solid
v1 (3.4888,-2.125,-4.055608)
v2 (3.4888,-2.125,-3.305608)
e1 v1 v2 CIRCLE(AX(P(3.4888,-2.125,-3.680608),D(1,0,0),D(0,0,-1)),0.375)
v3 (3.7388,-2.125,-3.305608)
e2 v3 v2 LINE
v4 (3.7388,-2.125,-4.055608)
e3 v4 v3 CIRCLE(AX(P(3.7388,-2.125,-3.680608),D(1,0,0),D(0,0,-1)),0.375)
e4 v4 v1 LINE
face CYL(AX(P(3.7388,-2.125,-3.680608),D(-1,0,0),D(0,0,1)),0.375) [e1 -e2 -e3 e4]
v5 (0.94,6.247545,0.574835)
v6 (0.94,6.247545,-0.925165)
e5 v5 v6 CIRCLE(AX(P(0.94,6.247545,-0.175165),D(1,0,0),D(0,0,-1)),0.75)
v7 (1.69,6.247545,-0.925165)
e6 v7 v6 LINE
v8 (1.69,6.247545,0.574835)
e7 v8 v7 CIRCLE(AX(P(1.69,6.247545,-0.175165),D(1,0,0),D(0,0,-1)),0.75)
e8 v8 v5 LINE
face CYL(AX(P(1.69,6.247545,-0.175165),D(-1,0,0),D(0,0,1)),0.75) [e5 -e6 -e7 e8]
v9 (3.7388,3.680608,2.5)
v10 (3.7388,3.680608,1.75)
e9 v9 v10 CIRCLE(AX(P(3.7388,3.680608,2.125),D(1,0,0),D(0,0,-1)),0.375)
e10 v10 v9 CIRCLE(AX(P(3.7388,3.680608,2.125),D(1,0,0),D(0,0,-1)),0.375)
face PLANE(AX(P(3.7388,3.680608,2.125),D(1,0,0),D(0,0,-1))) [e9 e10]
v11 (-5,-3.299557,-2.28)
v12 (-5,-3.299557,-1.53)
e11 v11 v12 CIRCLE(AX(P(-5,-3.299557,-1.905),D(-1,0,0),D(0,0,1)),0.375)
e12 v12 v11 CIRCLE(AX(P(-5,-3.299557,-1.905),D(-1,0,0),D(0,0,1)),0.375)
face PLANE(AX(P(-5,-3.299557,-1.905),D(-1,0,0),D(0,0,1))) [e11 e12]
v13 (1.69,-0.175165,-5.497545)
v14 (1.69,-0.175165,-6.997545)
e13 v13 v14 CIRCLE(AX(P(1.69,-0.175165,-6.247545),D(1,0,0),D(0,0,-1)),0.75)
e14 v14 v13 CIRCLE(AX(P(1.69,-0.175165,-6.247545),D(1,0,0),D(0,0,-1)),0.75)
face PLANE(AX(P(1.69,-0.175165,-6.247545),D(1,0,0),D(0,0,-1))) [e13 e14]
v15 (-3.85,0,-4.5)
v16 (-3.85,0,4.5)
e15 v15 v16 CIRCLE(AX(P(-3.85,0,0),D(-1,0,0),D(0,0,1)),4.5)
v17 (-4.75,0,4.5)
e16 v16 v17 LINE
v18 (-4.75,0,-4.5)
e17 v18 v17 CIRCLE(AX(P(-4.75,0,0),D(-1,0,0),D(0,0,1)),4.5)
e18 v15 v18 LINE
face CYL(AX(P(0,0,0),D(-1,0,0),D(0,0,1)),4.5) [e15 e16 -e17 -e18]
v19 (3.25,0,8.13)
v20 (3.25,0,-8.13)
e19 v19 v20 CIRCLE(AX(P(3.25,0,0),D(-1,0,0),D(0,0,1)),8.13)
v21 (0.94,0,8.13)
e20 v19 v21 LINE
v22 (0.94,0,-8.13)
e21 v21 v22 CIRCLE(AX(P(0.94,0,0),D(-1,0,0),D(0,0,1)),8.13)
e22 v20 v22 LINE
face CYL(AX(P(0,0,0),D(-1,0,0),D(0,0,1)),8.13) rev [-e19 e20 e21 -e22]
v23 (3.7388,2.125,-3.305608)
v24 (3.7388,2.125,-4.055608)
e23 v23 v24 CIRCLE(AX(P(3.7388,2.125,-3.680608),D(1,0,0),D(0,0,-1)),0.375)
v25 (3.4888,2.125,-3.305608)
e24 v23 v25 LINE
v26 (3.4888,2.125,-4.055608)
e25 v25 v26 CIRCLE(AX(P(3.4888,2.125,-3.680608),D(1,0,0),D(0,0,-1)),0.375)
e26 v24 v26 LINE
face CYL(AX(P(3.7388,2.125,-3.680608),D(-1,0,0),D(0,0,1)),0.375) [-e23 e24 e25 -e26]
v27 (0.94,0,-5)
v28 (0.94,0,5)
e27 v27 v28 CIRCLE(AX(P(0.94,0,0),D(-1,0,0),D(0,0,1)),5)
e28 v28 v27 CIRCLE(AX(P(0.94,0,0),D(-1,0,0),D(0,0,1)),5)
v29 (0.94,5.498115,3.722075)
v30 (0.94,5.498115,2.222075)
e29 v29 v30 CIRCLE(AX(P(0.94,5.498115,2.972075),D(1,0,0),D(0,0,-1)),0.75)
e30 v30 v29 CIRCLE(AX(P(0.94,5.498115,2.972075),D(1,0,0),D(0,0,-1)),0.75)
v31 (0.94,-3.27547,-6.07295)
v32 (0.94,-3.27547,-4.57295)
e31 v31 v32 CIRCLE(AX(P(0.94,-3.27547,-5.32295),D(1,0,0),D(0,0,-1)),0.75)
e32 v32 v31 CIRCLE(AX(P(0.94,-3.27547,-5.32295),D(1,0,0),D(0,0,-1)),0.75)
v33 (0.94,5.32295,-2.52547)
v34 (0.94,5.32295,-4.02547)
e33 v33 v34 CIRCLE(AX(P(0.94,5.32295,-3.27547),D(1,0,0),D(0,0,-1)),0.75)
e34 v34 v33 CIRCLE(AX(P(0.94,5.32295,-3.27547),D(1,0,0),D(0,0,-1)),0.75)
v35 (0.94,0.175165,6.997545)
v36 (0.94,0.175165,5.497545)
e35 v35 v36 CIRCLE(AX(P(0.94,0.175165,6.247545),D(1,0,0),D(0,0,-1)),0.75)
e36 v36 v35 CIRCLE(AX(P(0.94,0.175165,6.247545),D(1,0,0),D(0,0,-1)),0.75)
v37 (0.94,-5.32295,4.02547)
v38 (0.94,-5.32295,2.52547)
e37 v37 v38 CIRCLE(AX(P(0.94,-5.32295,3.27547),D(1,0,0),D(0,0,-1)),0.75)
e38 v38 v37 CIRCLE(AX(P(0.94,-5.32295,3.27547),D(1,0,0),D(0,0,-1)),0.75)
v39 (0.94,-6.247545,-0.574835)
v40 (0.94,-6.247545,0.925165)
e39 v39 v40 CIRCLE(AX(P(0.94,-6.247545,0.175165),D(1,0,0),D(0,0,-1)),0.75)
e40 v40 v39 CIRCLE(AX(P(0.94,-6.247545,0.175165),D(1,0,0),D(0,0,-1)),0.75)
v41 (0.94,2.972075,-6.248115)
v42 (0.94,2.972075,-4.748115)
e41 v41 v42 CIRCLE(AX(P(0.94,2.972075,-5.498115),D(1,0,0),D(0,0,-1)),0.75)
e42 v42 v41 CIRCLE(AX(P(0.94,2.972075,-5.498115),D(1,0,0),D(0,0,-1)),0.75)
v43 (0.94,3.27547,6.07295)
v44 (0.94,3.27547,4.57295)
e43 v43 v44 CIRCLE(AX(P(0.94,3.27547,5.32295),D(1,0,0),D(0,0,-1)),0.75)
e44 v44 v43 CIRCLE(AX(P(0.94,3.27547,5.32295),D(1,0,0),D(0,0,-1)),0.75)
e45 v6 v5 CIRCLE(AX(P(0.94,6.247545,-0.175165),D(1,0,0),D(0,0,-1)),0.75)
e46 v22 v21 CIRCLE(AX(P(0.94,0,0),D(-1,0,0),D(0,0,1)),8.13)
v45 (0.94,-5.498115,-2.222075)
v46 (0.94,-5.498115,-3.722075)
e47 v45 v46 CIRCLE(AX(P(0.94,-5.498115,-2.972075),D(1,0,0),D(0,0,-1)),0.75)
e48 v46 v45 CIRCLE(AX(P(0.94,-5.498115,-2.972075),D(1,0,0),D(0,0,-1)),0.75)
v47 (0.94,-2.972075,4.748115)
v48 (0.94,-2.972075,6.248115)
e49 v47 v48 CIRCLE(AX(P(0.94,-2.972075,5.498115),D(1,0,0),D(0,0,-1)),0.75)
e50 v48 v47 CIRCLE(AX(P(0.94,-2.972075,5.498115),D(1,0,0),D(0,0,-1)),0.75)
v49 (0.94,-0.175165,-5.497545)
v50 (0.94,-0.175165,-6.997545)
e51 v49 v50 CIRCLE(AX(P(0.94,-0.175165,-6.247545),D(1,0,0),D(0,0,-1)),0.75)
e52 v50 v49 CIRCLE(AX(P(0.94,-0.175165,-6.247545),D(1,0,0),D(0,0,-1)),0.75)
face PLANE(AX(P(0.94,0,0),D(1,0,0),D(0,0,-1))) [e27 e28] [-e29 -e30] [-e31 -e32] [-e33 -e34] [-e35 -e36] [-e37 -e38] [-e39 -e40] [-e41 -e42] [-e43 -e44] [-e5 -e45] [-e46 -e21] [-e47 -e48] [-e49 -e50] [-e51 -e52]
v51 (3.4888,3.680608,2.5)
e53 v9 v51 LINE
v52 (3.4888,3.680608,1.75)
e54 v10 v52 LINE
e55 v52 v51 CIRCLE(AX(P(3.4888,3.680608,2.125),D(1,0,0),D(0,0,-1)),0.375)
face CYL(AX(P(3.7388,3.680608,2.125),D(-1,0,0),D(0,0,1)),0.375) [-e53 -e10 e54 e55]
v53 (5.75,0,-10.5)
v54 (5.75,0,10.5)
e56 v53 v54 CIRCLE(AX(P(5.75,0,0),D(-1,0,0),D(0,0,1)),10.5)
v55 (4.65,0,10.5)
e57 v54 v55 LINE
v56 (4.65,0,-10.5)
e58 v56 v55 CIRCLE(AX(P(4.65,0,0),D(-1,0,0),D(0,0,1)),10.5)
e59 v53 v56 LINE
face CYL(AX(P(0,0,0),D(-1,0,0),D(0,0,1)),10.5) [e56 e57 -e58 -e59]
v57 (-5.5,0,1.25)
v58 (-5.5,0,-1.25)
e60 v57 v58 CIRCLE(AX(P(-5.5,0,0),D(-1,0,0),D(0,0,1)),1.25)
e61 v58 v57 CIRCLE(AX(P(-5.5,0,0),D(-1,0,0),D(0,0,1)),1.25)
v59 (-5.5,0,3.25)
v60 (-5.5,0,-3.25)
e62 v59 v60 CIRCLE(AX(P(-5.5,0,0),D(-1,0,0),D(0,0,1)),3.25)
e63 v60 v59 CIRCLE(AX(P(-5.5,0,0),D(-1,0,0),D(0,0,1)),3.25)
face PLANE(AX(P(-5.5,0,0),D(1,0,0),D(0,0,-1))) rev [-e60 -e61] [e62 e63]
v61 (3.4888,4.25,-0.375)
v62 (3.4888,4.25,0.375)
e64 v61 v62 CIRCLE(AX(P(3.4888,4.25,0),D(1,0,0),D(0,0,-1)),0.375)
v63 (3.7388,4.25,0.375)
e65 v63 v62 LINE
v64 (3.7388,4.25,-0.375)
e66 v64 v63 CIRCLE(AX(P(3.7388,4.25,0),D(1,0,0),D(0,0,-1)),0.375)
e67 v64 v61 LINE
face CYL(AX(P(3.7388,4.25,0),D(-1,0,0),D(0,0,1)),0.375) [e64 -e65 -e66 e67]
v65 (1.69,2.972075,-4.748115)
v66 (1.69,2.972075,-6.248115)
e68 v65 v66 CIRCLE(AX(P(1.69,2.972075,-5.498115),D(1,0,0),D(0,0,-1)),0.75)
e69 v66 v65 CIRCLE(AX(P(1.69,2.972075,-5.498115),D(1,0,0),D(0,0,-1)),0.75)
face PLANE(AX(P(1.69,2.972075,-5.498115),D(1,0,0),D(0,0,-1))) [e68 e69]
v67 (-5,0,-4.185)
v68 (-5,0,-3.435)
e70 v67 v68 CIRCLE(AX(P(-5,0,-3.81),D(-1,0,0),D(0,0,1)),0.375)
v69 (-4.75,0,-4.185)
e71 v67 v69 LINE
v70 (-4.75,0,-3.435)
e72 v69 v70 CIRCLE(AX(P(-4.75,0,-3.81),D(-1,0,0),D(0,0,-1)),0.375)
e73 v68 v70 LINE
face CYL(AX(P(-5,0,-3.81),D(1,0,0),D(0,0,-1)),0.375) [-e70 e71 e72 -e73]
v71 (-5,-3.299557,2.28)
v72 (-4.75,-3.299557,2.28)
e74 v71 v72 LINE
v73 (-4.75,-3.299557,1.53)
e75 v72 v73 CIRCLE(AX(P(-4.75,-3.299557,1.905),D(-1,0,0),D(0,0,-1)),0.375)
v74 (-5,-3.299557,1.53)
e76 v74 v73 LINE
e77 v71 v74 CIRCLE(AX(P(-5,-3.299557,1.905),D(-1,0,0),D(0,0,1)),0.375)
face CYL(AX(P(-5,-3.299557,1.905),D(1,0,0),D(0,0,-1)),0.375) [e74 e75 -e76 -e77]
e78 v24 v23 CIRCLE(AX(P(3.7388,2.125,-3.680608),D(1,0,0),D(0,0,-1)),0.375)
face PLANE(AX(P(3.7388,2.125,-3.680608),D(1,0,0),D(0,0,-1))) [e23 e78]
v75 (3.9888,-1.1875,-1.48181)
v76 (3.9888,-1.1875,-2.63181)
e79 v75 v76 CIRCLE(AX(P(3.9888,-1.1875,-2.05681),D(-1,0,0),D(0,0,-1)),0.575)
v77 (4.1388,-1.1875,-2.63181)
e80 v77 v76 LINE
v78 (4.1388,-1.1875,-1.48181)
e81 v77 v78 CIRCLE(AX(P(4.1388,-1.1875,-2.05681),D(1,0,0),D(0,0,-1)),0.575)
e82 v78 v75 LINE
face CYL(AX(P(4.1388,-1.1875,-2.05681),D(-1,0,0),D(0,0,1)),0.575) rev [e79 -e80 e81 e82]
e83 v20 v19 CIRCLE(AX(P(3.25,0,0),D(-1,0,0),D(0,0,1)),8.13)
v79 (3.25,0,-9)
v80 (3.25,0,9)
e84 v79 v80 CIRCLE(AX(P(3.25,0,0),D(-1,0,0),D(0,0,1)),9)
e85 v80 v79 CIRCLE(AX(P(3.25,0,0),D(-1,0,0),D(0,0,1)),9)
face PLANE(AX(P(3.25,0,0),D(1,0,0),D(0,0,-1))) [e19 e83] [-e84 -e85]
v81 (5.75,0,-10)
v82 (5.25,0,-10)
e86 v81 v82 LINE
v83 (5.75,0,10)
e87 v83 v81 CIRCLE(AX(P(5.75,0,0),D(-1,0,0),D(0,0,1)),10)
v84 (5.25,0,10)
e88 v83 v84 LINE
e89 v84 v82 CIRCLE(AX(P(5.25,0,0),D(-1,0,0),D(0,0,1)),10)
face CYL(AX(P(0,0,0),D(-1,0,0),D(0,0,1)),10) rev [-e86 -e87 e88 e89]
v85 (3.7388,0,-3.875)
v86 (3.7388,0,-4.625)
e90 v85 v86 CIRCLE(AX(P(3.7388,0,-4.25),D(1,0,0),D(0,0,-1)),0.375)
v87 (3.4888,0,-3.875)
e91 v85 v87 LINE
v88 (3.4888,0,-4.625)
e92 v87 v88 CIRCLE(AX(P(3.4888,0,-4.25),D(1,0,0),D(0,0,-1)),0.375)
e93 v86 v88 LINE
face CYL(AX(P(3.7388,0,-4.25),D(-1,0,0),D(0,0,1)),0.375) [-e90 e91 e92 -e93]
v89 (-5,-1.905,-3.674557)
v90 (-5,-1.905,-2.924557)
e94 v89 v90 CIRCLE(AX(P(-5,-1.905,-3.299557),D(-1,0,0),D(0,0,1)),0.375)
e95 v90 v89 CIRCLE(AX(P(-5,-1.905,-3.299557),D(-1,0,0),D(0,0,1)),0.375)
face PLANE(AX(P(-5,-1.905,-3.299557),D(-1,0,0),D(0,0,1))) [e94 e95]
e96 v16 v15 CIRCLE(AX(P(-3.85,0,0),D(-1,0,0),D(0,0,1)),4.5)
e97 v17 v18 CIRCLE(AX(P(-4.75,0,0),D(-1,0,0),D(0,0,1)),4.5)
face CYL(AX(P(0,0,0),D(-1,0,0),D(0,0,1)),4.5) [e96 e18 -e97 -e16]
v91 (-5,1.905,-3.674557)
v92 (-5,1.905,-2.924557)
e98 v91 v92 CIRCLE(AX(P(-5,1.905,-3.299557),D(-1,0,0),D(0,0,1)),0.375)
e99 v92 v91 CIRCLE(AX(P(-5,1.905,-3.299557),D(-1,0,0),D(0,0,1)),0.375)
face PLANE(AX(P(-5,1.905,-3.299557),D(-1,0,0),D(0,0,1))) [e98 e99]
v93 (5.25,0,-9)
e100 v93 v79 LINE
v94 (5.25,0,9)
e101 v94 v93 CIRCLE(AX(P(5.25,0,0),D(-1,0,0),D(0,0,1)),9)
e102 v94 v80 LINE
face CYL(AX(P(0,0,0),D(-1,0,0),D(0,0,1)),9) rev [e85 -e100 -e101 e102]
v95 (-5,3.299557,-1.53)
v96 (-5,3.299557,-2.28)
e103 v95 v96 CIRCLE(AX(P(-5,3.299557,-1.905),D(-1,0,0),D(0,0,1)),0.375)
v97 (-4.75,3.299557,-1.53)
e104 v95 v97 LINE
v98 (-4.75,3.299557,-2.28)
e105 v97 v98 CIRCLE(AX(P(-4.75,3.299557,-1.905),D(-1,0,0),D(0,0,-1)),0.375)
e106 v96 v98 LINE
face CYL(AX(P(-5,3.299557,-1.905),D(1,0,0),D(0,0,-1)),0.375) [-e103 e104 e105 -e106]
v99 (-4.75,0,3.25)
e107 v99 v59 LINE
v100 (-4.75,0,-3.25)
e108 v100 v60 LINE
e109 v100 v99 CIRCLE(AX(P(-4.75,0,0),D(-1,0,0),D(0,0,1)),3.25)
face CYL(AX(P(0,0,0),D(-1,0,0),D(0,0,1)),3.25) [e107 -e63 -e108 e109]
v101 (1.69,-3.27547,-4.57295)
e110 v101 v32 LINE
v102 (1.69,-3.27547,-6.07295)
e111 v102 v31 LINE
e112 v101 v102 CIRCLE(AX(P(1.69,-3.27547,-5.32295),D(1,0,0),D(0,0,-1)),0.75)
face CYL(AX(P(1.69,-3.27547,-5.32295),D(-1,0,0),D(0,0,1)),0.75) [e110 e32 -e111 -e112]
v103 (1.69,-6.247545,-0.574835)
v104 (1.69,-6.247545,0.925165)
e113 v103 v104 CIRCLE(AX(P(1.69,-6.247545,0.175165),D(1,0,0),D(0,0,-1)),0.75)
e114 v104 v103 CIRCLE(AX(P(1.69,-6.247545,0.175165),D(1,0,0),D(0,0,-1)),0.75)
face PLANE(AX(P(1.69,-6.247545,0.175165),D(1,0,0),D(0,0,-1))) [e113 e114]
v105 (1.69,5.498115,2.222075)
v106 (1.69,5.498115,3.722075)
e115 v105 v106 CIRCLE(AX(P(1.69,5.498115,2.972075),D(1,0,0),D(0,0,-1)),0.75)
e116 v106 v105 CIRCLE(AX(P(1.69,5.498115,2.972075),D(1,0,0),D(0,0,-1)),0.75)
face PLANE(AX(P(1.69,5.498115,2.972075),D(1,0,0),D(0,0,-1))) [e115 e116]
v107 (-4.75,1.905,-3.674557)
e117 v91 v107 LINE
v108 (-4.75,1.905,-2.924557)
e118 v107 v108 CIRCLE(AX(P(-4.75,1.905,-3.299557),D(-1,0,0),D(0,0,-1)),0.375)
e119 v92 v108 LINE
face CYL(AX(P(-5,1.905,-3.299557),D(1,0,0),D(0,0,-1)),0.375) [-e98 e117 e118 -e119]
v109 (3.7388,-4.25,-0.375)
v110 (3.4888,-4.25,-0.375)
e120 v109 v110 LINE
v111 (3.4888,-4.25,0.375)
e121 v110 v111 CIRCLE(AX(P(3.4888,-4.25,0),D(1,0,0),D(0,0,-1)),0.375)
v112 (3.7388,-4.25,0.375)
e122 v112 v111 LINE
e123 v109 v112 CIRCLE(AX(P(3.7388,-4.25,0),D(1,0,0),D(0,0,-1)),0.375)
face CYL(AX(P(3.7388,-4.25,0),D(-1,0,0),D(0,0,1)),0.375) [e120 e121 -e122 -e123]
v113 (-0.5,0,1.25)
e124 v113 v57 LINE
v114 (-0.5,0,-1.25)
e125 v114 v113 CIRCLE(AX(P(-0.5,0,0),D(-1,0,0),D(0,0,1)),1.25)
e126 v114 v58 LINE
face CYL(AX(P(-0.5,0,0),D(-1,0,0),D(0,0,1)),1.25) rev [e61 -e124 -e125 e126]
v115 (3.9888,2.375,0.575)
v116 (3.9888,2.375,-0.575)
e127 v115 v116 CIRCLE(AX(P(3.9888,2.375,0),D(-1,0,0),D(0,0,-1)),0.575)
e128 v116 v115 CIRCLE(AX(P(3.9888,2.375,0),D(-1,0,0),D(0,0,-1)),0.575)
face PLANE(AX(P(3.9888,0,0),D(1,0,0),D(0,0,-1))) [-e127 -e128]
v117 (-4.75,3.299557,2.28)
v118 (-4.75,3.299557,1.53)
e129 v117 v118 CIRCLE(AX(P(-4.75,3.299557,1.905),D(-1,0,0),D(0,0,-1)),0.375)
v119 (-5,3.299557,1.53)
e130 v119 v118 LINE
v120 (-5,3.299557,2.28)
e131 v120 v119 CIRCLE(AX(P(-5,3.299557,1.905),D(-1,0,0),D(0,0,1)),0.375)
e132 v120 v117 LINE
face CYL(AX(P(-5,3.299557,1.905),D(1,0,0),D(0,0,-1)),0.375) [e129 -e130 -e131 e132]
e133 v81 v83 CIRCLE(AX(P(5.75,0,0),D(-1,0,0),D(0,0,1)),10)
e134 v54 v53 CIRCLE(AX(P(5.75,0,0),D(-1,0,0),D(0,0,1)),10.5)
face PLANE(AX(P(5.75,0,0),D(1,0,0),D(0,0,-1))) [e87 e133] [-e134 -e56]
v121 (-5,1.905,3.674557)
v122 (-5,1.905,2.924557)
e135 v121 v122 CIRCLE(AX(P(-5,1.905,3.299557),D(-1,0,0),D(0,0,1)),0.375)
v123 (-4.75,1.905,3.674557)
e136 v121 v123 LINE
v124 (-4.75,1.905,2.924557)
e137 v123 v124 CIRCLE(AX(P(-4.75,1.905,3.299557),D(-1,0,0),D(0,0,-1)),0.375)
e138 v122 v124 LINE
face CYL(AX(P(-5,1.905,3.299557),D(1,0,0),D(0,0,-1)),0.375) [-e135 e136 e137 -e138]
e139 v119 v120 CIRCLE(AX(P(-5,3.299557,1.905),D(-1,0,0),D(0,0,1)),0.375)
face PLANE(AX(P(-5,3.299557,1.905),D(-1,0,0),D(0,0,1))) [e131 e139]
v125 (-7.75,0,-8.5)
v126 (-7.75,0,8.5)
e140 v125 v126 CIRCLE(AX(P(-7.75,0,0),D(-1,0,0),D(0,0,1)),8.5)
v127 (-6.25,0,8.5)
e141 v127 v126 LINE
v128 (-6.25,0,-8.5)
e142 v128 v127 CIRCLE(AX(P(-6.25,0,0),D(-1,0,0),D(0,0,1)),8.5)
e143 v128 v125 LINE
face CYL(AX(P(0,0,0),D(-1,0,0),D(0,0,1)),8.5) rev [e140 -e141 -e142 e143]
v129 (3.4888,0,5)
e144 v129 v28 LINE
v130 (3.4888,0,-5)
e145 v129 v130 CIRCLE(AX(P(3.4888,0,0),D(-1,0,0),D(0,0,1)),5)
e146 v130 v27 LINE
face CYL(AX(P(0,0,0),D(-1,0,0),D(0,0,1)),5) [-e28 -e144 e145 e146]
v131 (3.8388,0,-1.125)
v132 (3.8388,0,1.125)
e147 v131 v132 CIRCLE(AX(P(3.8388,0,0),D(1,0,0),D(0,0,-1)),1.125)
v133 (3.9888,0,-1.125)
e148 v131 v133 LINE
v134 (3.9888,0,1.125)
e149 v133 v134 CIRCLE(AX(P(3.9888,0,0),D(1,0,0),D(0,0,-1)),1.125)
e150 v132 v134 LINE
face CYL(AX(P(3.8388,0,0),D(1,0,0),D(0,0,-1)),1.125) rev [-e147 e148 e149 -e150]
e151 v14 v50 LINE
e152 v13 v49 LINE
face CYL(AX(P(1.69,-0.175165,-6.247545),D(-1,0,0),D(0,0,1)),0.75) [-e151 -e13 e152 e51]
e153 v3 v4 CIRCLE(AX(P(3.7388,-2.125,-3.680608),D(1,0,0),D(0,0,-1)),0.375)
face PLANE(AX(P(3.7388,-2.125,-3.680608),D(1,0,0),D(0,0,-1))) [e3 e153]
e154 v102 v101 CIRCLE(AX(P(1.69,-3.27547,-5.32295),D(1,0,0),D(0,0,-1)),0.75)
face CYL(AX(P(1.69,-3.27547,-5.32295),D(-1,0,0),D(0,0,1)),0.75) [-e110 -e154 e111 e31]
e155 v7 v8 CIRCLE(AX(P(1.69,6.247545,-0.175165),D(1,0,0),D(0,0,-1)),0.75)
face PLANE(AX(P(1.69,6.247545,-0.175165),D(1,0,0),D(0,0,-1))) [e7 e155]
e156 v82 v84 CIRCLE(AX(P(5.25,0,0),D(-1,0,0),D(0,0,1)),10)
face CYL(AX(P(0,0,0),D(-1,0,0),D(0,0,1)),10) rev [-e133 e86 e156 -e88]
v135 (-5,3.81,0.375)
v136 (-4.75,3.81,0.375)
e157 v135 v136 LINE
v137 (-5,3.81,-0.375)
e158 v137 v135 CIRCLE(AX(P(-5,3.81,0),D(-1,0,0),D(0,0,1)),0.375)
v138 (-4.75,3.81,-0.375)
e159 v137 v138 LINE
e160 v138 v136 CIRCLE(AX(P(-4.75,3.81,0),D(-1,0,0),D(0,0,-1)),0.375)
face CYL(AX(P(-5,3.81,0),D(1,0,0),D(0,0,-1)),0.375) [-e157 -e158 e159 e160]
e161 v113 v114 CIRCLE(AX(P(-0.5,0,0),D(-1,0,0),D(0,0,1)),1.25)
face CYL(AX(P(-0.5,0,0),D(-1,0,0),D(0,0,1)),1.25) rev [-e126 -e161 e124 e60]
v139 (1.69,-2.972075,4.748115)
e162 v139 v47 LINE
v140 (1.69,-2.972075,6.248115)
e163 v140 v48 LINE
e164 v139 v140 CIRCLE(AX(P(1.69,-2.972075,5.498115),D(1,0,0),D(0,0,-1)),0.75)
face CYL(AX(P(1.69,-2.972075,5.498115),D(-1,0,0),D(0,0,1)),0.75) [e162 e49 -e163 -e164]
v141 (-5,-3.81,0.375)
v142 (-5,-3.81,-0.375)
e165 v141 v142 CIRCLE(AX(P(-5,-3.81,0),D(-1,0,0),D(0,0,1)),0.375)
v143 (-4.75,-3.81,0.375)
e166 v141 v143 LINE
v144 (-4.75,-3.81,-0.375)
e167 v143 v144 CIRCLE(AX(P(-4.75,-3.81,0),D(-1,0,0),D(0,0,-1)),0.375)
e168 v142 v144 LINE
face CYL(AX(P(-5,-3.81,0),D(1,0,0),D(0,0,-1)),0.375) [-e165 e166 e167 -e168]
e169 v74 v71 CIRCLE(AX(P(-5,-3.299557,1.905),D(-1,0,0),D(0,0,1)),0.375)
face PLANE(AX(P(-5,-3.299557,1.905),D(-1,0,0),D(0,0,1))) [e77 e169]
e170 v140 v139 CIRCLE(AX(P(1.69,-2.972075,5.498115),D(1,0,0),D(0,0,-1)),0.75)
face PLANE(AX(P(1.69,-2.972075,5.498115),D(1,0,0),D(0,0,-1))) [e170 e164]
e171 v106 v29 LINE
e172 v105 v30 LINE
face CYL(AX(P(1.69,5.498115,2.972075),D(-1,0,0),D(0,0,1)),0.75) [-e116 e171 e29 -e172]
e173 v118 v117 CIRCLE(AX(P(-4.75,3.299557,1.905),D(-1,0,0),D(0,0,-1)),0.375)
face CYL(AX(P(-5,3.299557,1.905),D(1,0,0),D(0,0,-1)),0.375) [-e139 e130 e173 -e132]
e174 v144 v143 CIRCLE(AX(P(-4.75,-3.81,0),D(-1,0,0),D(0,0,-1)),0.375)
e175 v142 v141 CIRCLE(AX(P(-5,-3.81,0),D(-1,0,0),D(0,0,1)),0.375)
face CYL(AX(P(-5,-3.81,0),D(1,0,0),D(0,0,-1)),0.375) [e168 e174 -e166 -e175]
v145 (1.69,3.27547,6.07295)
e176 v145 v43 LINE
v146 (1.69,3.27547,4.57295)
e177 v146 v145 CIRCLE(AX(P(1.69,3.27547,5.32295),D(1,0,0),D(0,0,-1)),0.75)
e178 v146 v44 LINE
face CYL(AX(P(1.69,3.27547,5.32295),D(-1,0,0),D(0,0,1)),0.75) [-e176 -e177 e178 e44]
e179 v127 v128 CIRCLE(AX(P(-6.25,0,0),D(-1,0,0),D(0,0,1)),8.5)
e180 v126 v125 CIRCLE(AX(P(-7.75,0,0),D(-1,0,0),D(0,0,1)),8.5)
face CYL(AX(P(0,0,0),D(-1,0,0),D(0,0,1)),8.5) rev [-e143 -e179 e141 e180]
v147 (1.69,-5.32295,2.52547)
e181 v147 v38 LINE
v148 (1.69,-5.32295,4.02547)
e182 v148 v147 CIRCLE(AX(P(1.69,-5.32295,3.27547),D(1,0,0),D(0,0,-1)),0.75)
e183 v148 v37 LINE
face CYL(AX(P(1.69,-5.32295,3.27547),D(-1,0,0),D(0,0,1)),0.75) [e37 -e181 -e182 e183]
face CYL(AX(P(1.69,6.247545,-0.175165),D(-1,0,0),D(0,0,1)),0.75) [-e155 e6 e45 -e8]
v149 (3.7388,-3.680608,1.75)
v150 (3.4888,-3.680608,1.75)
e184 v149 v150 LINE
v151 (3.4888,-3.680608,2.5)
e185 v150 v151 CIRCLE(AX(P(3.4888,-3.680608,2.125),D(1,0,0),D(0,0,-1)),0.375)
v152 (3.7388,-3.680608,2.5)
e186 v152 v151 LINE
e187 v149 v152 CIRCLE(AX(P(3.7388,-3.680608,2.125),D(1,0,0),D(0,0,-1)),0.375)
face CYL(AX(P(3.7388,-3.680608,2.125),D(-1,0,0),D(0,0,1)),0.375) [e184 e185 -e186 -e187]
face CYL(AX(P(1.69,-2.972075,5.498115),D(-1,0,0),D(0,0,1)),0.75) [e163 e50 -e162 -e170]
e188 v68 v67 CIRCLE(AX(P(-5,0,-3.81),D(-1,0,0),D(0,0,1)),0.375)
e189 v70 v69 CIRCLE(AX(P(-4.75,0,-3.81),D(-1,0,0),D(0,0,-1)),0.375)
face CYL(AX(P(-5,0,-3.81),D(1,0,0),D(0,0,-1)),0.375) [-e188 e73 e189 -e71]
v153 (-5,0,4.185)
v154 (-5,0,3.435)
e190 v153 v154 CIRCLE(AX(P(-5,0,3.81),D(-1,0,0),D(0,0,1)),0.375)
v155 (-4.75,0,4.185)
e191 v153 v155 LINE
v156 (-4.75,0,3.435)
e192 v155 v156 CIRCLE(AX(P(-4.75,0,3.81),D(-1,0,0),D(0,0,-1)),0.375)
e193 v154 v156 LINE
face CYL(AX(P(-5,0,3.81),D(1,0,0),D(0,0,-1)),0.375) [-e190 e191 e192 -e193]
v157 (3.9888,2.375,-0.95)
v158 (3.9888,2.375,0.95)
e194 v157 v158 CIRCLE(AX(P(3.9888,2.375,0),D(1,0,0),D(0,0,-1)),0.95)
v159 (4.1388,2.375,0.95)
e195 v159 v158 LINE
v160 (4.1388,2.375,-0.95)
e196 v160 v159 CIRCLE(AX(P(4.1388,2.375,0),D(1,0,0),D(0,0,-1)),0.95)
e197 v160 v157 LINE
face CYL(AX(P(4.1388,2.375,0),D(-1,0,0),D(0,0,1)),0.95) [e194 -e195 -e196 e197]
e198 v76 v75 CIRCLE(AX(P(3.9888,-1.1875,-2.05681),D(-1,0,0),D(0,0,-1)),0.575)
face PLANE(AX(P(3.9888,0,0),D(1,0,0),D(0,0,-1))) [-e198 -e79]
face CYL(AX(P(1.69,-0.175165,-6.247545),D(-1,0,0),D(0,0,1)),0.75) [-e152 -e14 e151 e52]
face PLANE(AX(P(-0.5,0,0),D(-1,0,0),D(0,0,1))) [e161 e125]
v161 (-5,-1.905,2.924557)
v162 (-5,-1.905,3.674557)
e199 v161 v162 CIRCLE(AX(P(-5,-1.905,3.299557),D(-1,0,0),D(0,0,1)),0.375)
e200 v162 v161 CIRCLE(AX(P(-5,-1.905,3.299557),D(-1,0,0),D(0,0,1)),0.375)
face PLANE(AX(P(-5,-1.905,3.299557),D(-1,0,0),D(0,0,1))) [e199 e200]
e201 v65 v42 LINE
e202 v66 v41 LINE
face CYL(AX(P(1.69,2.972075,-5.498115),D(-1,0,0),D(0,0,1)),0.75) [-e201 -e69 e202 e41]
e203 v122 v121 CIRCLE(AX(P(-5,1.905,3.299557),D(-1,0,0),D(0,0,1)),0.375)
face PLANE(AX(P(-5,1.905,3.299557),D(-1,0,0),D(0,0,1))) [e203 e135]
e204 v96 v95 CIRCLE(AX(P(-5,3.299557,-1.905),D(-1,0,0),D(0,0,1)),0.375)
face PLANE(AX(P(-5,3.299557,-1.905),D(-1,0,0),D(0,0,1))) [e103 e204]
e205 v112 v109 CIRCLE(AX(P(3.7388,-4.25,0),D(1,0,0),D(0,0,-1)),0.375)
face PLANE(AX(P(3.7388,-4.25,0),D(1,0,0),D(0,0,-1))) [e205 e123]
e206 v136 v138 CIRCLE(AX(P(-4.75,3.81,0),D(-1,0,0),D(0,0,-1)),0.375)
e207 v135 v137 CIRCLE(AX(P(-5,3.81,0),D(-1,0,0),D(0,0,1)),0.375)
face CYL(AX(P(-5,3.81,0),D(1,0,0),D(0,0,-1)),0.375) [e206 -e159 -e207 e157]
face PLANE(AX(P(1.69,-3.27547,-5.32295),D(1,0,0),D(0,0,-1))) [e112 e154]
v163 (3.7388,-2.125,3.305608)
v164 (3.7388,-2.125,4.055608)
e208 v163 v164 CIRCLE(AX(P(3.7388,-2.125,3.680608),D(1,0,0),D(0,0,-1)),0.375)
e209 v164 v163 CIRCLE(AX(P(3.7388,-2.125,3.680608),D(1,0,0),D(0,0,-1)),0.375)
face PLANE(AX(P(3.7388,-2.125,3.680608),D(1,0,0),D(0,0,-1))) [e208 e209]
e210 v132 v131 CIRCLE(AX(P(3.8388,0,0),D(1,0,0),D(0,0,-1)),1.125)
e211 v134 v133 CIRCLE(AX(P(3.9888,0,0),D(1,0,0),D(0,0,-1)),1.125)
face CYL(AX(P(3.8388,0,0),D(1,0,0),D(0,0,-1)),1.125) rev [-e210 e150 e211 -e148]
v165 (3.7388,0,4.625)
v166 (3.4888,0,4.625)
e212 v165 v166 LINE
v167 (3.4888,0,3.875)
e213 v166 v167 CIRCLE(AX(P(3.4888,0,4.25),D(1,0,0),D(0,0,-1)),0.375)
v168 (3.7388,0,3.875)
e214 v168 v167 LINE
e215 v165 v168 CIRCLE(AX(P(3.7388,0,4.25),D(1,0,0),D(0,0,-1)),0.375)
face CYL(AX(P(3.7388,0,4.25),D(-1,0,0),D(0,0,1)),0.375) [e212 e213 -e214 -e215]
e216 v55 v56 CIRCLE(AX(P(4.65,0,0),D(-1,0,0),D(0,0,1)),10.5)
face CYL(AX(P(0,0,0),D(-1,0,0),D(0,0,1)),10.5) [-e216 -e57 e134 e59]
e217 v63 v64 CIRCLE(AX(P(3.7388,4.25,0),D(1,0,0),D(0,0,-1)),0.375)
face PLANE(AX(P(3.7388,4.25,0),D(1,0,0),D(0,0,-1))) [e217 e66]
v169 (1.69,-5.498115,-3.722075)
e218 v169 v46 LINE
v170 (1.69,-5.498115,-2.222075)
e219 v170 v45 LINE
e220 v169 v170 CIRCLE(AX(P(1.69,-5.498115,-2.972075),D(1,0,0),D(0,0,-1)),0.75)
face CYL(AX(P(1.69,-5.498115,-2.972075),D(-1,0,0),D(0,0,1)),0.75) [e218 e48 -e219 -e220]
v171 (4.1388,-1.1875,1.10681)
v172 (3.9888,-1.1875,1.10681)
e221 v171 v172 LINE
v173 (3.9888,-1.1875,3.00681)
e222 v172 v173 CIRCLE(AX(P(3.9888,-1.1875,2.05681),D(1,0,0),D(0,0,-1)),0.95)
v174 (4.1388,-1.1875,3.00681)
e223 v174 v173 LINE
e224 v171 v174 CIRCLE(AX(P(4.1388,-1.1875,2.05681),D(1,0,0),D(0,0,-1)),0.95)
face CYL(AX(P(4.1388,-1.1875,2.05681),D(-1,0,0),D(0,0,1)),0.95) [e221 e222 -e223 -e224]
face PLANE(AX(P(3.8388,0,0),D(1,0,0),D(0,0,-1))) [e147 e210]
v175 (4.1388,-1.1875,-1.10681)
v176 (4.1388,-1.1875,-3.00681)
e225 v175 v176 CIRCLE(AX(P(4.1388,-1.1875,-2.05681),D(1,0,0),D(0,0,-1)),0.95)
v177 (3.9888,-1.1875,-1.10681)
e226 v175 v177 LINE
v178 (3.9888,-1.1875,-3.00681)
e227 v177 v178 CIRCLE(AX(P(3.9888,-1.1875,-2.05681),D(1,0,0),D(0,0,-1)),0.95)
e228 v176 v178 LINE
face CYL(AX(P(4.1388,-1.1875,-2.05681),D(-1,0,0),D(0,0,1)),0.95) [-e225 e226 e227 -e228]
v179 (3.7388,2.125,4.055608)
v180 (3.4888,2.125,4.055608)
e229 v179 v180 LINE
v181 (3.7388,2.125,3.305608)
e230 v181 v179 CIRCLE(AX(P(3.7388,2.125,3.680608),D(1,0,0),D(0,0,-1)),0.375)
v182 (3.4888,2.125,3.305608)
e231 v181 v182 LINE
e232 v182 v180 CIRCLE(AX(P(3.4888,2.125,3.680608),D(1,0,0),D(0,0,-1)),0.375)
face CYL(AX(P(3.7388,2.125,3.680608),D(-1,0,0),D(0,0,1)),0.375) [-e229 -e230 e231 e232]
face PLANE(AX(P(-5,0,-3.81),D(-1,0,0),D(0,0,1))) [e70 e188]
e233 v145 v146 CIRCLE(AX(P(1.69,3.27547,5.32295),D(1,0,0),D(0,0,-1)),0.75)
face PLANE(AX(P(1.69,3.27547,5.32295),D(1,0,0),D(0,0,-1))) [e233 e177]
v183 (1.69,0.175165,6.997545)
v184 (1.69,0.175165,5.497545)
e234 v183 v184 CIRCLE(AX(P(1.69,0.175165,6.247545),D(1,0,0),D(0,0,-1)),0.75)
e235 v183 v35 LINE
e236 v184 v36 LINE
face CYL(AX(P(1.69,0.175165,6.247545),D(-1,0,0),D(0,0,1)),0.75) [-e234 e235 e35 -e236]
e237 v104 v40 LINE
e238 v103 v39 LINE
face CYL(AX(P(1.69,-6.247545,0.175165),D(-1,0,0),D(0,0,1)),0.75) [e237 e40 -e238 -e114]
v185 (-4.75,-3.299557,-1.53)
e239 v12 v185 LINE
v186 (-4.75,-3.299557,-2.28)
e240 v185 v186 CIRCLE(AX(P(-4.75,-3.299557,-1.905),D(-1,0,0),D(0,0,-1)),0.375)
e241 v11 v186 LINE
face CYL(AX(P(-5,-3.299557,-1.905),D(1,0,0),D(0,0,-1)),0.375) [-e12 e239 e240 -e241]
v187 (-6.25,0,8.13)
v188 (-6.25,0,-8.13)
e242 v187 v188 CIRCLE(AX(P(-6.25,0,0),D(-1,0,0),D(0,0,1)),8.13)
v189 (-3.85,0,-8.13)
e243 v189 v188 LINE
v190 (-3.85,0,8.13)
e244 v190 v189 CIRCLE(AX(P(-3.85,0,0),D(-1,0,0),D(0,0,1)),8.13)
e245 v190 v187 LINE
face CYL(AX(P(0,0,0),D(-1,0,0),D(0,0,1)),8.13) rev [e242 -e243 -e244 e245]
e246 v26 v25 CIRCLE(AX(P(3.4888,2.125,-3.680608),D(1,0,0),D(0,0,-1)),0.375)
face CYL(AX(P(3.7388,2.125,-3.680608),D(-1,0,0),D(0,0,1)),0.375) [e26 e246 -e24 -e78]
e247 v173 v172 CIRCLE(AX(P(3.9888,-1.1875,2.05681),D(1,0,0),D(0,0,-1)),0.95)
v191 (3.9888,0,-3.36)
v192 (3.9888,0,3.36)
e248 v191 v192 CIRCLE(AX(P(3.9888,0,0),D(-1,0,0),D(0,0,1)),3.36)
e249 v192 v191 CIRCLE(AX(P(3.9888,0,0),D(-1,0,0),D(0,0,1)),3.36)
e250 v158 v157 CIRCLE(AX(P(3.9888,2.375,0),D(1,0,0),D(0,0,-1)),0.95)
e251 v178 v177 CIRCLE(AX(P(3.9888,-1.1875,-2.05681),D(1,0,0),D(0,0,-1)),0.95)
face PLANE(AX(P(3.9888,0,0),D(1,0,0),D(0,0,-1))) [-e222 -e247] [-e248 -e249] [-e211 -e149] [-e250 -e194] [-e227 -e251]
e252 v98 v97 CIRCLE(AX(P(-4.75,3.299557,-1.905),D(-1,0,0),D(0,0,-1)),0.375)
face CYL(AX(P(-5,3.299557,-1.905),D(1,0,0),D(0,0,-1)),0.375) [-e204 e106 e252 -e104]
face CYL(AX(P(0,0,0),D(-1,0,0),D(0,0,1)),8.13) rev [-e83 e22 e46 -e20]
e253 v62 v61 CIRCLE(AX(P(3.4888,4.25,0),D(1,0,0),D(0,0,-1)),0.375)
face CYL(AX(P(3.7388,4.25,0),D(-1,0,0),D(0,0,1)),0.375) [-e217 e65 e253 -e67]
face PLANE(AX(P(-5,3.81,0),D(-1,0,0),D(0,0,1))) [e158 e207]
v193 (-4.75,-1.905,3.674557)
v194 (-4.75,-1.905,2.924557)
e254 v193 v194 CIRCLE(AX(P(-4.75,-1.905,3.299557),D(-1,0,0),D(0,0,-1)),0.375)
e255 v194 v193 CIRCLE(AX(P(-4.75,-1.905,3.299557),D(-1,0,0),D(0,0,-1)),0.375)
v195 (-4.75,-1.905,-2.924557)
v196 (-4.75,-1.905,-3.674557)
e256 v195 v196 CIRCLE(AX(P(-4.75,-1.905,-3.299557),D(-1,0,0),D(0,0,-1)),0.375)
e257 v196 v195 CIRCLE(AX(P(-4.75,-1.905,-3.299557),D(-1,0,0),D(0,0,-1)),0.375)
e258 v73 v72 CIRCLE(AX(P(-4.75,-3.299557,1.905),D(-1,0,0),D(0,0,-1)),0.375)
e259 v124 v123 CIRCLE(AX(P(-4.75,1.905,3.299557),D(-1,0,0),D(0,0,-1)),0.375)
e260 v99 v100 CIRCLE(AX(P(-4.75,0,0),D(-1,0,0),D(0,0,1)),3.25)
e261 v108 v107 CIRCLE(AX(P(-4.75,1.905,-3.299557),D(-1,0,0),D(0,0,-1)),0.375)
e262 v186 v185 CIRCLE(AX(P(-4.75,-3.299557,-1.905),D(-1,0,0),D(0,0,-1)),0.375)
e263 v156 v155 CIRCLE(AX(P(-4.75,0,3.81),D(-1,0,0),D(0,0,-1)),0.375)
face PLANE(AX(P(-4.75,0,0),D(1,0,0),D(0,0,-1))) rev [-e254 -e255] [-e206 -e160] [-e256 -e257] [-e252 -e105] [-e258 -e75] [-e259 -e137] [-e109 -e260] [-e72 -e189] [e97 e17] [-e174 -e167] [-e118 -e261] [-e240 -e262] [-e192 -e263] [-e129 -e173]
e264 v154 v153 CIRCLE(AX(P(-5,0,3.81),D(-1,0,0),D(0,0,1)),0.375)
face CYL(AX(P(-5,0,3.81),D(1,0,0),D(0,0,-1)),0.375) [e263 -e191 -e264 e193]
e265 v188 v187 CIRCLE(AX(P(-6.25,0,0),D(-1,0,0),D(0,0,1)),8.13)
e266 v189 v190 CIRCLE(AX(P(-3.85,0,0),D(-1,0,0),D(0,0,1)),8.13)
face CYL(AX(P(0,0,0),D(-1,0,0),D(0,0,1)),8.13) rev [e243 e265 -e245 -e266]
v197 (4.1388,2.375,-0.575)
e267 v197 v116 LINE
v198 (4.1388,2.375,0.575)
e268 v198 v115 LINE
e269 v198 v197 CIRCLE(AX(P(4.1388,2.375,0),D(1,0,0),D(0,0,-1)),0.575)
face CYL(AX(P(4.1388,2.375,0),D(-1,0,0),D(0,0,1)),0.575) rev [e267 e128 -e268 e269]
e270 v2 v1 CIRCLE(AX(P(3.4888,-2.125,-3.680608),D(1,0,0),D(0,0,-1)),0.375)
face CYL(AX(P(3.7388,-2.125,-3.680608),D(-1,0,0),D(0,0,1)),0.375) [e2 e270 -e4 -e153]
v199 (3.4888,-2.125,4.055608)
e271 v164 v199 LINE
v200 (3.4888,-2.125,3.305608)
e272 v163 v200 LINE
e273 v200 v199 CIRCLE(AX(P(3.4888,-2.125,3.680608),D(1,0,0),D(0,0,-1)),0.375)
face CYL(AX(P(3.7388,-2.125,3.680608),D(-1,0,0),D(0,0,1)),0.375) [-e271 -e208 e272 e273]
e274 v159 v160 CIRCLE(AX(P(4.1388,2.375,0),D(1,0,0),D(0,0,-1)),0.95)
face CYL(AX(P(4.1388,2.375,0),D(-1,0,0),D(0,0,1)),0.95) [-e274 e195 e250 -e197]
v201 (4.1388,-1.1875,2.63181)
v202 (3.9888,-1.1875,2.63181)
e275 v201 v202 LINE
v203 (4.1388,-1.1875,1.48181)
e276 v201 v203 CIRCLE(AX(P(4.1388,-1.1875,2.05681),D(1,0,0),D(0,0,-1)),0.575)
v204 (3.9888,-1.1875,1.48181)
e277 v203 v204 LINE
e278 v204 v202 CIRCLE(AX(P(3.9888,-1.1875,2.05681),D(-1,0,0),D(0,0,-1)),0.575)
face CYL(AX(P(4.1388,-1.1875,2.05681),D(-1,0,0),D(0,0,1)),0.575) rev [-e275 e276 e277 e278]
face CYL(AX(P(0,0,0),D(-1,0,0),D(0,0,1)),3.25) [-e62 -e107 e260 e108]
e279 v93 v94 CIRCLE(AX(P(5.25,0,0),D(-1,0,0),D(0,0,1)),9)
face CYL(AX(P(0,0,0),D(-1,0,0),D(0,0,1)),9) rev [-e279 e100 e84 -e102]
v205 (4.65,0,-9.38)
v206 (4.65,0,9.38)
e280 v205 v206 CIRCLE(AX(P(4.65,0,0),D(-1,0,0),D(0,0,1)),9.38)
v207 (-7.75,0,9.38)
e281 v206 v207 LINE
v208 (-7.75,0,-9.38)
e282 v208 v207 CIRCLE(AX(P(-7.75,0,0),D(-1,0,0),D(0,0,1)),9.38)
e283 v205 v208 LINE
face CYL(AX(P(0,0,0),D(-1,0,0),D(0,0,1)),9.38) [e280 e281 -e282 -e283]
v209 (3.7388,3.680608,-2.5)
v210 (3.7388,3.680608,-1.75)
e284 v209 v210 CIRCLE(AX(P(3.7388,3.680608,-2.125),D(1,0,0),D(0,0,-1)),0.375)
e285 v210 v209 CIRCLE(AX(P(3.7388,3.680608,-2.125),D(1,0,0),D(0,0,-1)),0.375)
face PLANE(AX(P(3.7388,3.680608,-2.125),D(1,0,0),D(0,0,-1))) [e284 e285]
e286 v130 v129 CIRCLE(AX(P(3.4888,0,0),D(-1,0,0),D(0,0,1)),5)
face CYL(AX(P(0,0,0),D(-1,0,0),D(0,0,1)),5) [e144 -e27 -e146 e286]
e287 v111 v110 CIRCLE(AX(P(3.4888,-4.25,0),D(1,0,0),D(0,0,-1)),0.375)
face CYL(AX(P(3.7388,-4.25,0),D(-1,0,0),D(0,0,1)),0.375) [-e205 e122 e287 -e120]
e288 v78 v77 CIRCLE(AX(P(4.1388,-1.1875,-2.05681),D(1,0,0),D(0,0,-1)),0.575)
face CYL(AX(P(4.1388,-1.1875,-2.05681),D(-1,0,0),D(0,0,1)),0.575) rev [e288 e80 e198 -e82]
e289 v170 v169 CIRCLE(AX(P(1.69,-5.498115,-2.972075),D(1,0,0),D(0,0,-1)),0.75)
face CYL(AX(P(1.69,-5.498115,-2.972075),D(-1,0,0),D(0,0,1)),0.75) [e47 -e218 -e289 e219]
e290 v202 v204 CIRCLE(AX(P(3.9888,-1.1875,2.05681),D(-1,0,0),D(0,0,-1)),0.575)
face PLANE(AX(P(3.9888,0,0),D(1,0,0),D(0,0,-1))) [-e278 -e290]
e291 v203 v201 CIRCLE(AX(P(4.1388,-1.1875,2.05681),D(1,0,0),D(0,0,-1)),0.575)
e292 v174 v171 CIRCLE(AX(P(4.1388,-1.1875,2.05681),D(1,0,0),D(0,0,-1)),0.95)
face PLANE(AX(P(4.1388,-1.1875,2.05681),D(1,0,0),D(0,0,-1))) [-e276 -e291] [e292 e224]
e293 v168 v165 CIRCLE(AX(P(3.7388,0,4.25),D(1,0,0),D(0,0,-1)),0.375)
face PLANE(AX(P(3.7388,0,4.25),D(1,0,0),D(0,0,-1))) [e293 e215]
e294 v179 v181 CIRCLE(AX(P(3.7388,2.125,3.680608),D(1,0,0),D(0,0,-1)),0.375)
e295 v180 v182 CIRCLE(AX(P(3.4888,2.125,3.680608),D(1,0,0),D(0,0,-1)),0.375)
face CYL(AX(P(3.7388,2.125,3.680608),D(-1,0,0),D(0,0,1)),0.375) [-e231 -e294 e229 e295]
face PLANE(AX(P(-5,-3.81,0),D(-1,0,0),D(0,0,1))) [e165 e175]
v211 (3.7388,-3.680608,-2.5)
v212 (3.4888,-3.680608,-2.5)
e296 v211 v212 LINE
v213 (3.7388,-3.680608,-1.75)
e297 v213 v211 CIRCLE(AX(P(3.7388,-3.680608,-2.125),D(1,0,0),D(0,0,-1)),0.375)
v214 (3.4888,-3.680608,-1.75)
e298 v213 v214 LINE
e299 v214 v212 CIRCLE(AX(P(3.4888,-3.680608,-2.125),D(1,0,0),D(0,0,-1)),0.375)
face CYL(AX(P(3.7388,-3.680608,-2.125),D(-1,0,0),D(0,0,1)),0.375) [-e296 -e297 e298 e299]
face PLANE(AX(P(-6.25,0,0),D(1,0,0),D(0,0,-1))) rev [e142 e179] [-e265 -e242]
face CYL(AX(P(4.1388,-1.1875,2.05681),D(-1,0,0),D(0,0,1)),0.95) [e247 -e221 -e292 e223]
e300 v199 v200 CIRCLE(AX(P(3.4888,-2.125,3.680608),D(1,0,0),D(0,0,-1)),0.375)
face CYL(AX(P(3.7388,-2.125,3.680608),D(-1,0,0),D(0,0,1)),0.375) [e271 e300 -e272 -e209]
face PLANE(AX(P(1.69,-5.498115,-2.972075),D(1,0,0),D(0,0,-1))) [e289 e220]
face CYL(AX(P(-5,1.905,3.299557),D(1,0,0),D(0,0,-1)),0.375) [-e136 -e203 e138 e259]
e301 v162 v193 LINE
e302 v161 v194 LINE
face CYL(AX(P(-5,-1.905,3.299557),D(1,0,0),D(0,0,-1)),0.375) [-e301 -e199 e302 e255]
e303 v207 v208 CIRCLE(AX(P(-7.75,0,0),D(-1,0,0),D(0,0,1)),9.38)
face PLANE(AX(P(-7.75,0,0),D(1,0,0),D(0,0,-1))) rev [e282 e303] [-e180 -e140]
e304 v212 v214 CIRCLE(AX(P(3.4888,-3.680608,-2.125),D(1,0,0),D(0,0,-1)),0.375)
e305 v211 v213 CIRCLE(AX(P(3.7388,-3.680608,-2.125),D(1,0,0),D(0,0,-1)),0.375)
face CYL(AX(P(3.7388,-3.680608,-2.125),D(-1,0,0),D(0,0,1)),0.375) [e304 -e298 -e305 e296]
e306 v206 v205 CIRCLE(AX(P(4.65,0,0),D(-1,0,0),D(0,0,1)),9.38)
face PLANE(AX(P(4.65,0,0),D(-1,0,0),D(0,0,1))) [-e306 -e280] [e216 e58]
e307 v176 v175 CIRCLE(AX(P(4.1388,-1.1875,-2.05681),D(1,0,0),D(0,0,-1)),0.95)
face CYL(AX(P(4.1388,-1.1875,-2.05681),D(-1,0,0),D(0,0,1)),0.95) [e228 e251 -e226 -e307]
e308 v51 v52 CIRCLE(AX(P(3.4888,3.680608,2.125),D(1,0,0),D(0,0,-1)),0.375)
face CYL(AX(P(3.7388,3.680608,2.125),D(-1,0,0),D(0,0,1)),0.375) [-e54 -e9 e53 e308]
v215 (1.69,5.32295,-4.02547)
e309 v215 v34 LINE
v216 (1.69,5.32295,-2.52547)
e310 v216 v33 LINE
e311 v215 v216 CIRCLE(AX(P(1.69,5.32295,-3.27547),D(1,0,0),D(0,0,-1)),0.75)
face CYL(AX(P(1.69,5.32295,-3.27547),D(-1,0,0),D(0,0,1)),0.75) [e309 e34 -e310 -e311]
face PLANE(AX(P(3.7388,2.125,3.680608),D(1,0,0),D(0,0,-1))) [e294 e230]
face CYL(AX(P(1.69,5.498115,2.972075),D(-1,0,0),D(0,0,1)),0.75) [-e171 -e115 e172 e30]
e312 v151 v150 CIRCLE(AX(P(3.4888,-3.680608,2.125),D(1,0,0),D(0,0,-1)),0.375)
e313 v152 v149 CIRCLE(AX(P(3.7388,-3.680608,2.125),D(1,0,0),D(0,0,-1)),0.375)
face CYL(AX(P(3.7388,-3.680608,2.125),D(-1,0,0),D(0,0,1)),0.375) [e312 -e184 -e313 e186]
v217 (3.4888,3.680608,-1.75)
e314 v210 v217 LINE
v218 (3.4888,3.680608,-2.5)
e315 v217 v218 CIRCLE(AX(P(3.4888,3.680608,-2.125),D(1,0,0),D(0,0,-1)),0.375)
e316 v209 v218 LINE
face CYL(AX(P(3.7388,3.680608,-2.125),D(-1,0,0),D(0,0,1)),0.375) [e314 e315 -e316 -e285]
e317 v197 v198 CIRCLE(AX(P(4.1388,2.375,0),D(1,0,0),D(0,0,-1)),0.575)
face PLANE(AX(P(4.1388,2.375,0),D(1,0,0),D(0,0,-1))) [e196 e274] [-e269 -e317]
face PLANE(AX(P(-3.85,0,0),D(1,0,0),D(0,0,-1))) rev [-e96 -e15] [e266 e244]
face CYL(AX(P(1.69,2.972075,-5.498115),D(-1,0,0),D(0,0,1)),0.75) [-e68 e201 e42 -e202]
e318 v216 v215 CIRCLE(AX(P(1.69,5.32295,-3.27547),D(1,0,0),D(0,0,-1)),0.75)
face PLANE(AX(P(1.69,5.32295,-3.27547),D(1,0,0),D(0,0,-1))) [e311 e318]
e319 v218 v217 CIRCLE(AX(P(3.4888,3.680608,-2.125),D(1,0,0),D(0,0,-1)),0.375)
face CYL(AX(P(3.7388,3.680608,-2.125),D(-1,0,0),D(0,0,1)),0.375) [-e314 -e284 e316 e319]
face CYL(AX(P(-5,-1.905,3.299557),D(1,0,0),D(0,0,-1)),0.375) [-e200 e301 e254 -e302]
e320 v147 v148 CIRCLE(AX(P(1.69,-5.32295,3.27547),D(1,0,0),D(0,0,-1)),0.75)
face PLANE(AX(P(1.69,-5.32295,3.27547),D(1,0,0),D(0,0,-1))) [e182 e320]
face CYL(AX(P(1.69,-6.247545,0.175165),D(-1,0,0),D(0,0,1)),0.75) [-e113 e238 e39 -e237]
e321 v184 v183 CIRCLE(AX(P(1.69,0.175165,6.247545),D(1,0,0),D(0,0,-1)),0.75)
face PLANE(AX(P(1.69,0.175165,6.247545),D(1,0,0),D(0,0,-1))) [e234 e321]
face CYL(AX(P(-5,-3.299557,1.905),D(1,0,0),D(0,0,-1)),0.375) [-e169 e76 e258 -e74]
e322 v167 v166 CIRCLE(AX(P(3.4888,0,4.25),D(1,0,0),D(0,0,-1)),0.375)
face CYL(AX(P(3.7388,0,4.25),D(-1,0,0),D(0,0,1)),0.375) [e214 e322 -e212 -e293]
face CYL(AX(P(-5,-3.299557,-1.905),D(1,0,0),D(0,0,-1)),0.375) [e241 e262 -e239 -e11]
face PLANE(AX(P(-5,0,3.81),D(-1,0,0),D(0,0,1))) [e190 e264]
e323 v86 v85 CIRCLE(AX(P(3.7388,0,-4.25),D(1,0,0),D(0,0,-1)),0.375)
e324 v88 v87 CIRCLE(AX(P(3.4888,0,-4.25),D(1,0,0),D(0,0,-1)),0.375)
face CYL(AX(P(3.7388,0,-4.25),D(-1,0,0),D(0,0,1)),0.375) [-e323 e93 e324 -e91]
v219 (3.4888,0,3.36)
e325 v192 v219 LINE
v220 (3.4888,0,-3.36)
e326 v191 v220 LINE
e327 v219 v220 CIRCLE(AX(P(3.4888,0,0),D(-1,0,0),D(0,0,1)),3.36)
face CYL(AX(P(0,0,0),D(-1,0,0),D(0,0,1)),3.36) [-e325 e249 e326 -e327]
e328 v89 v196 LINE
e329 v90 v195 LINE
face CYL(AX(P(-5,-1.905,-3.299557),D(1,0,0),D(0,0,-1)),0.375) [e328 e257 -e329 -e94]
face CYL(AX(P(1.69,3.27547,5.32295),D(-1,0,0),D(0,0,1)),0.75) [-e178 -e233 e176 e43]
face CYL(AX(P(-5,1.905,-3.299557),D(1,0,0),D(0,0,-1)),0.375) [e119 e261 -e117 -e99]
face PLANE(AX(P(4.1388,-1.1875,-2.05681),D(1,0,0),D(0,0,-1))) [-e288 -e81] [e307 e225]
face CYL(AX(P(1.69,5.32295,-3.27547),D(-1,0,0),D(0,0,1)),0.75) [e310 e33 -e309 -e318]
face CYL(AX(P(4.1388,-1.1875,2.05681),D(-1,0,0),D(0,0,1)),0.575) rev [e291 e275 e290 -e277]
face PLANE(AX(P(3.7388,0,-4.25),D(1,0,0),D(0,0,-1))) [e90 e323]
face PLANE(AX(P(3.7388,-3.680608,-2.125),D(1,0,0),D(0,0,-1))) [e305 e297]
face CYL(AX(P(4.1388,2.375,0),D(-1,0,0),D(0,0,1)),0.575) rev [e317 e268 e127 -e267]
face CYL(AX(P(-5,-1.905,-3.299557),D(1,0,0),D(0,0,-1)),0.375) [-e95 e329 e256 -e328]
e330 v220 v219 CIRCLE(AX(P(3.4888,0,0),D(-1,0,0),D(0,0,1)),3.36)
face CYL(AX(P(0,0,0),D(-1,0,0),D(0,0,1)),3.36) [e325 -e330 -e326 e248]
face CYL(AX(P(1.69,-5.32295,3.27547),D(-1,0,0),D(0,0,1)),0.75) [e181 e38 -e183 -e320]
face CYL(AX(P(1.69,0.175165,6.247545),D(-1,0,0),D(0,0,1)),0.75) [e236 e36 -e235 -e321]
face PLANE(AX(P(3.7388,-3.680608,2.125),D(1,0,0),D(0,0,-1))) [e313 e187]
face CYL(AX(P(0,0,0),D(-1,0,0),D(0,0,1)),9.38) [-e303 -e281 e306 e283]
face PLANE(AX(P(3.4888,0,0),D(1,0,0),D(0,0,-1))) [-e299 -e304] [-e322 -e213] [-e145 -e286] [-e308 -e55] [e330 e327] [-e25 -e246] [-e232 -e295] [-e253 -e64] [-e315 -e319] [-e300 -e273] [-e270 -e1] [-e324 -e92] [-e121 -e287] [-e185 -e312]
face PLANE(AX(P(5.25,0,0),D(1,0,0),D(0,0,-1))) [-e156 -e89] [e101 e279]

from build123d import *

# Parameters (mm, degrees)
OUTER_BOSS_RING_SKETCH_12X_1_5_R = 0.75
OUTER_BOSS_RING_12X_DEPTH        = 0.75
MIDDLE_BOSS_RING_SKETCH_12X_R    = 0.375
MIDDLE_BOSS_RING_12X_DEPTH       = 0.25
HUB_RECESS_SKETCH_2_25_R         = 1.125
HUB_RECESS_2_25_DEPTH            = 0.15
LUG_NUTS_SKETCH_3X_R             = 0.95
LUG_NUTS_SKETCH_3X_R_2           = 0.575
LUG_NUTS_3X_DEPTH                = 0.15
INNER_BOSS_RING_SKETCH_12X_R     = 0.375
INNER_BOSS_RING_12X_DEPTH        = 0.25
AXLE_BORE_SKETCH_2_5_R           = 1.25
AXLE_BORE_2_5_DEPTH              = 5


with BuildPart() as part:
    # Rim Profile Sketch → Rim Body Revolve (revolve)
    with BuildSketch(Plane.XY, mode=Mode.PRIVATE) as rim_body_revolve_sk:
        Polygon((4.65, 9.38), (0, 9.38), (-7.75, 9.38), (-7.75, 8.5), (-6.25, 8.5), (-6.25, 8.13), (-3.85, 8.13), (-3.85, 4.5), (-4.75, 4.5), (-4.75, 3.25), (-5.5, 3.25), (-5.5, 0), (3.988800196, 0), (3.988800196, 3.36), (3.488800196, 3.36), (3.488800196, 5), (0.94, 5), (0.94, 8.13), (3.25, 8.13), (3.25, 9), (5.25, 9), (5.25, 10), (5.75, 10), (5.75, 10.5), (4.65, 10.5), align=None)
    revolve(rim_body_revolve_sk.sketch.rotate(Axis((0, 0, 0), (1, 0, 0)), 90), axis=Axis((0, 0, 0), (1, 0, 0)))

    # Outer Boss Ring Sketch 12xØ1.5 → Outer Boss Ring 12x (add)
    with BuildSketch(Plane(origin=(0.94, 0, 0), x_dir=(0, 0, -1), z_dir=(1, 0, 0))):
        with Locations((0.17516481, 6.247544901)):
            Circle(OUTER_BOSS_RING_SKETCH_12X_1_5_R)
        with Locations((3.275469626, 5.32295019)):
            Circle(OUTER_BOSS_RING_SKETCH_12X_1_5_R)
        with Locations((5.498115001, 2.972075275)):
            Circle(OUTER_BOSS_RING_SKETCH_12X_1_5_R)
        with Locations((6.247544901, -0.17516481)):
            Circle(OUTER_BOSS_RING_SKETCH_12X_1_5_R)
        with Locations((5.32295019, -3.275469626)):
            Circle(OUTER_BOSS_RING_SKETCH_12X_1_5_R)
        with Locations((2.972075275, -5.498115001)):
            Circle(OUTER_BOSS_RING_SKETCH_12X_1_5_R)
        with Locations((-0.17516481, -6.247544901)):
            Circle(OUTER_BOSS_RING_SKETCH_12X_1_5_R)
        with Locations((-3.275469626, -5.32295019)):
            Circle(OUTER_BOSS_RING_SKETCH_12X_1_5_R)
        with Locations((-5.498115001, -2.972075275)):
            Circle(OUTER_BOSS_RING_SKETCH_12X_1_5_R)
        with Locations((-6.247544901, 0.17516481)):
            Circle(OUTER_BOSS_RING_SKETCH_12X_1_5_R)
        with Locations((-5.32295019, 3.275469626)):
            Circle(OUTER_BOSS_RING_SKETCH_12X_1_5_R)
        with Locations((-2.972075275, 5.498115001)):
            Circle(OUTER_BOSS_RING_SKETCH_12X_1_5_R)
    extrude(amount=OUTER_BOSS_RING_12X_DEPTH)

    # Middle Boss Ring Sketch 12x → Middle Boss Ring 12x (add)
    with BuildSketch(Plane(origin=(3.488800196, 0, 0), x_dir=(0, 0, -1), z_dir=(1, 0, 0))):
        with Locations((0, 4.25)):
            Circle(MIDDLE_BOSS_RING_SKETCH_12X_R)
        with Locations((2.125, 3.680607966)):
            Circle(MIDDLE_BOSS_RING_SKETCH_12X_R)
        with Locations((3.680607966, 2.125)):
            Circle(MIDDLE_BOSS_RING_SKETCH_12X_R)
        with Locations((4.25, 0)):
            Circle(MIDDLE_BOSS_RING_SKETCH_12X_R)
        with Locations((3.680607966, -2.125)):
            Circle(MIDDLE_BOSS_RING_SKETCH_12X_R)
        with Locations((2.125, -3.680607966)):
            Circle(MIDDLE_BOSS_RING_SKETCH_12X_R)
        with Locations((0, -4.25)):
            Circle(MIDDLE_BOSS_RING_SKETCH_12X_R)
        with Locations((-2.125, -3.680607966)):
            Circle(MIDDLE_BOSS_RING_SKETCH_12X_R)
        with Locations((-3.680607966, -2.125)):
            Circle(MIDDLE_BOSS_RING_SKETCH_12X_R)
        with Locations((-4.25, 0)):
            Circle(MIDDLE_BOSS_RING_SKETCH_12X_R)
        with Locations((-3.680607966, 2.125)):
            Circle(MIDDLE_BOSS_RING_SKETCH_12X_R)
        with Locations((-2.125, 3.680607966)):
            Circle(MIDDLE_BOSS_RING_SKETCH_12X_R)
    extrude(amount=MIDDLE_BOSS_RING_12X_DEPTH)

    # Hub Recess Sketch Ø2.25 → Hub Recess Ø2.25 (cut)
    with BuildSketch(Plane(origin=(3.988800196, 0, 0), x_dir=(0, 0, -1), z_dir=(1, 0, 0))):
        Circle(HUB_RECESS_SKETCH_2_25_R)
    extrude(amount=-HUB_RECESS_2_25_DEPTH, mode=Mode.SUBTRACT)

    # Lug Nuts Sketch 3x → Lug Nuts 3x (add)
    # profile 1 of 3: a face of its own
    with BuildSketch(Plane(origin=(3.988800196, 0, 0), x_dir=(0, 0, -1), z_dir=(1, 0, 0))):
        with Locations((0, 2.375)):
            Circle(LUG_NUTS_SKETCH_3X_R)
        with Locations((0, 2.375)):
            Circle(LUG_NUTS_SKETCH_3X_R_2, mode=Mode.SUBTRACT)
    # profile 2 of 3: a face of its own
    with BuildSketch(Plane(origin=(3.988800196, 0, 0), x_dir=(0, 0, -1), z_dir=(1, 0, 0))):
        with Locations((2.056810334, -1.1875)):
            Circle(LUG_NUTS_SKETCH_3X_R)
        with Locations((2.056810334, -1.1875)):
            Circle(LUG_NUTS_SKETCH_3X_R_2, mode=Mode.SUBTRACT)
    # profile 3 of 3: a face of its own
    with BuildSketch(Plane(origin=(3.988800196, 0, 0), x_dir=(0, 0, -1), z_dir=(1, 0, 0))):
        with Locations((-2.056810334, -1.1875)):
            Circle(LUG_NUTS_SKETCH_3X_R)
        with Locations((-2.056810334, -1.1875)):
            Circle(LUG_NUTS_SKETCH_3X_R_2, mode=Mode.SUBTRACT)
    extrude(amount=LUG_NUTS_3X_DEPTH)

    # Inner Boss Ring Sketch 12x → Inner Boss Ring 12x (add)
    with BuildSketch(Plane.ZY.offset(4.75)):
        with Locations(Location((0, 3.81, 0), (0, 0, 180))):
            Circle(INNER_BOSS_RING_SKETCH_12X_R)
        with Locations(Location((1.905, 3.299556788, 0), (0, 0, 180))):
            Circle(INNER_BOSS_RING_SKETCH_12X_R)
        with Locations(Location((3.299556788, 1.905, 0), (0, 0, 180))):
            Circle(INNER_BOSS_RING_SKETCH_12X_R)
        with Locations(Location((3.81, 0, 0), (0, 0, 180))):
            Circle(INNER_BOSS_RING_SKETCH_12X_R)
        with Locations(Location((3.299556788, -1.905, 0), (0, 0, 180))):
            Circle(INNER_BOSS_RING_SKETCH_12X_R)
        with Locations(Location((1.905, -3.299556788, 0), (0, 0, 180))):
            Circle(INNER_BOSS_RING_SKETCH_12X_R)
        with Locations(Location((0, -3.81, 0), (0, 0, 180))):
            Circle(INNER_BOSS_RING_SKETCH_12X_R)
        with Locations(Location((-1.905, -3.299556788, 0), (0, 0, 180))):
            Circle(INNER_BOSS_RING_SKETCH_12X_R)
        with Locations(Location((-3.299556788, -1.905, 0), (0, 0, 180))):
            Circle(INNER_BOSS_RING_SKETCH_12X_R)
        with Locations(Location((-3.81, 0, 0), (0, 0, 180))):
            Circle(INNER_BOSS_RING_SKETCH_12X_R)
        with Locations(Location((-3.299556788, 1.905, 0), (0, 0, 180))):
            Circle(INNER_BOSS_RING_SKETCH_12X_R)
        with Locations(Location((-1.905, 3.299556788, 0), (0, 0, 180))):
            Circle(INNER_BOSS_RING_SKETCH_12X_R)
    extrude(amount=INNER_BOSS_RING_12X_DEPTH)

    # Axle Bore Sketch Ø2.5 → Axle Bore Ø2.5 (cut)
    with BuildSketch(Plane.ZY.offset(5.5)):
        Circle(AXLE_BORE_SKETCH_2_5_R)
    extrude(amount=-AXLE_BORE_2_5_DEPTH, mode=Mode.SUBTRACT)


solid = part.part
